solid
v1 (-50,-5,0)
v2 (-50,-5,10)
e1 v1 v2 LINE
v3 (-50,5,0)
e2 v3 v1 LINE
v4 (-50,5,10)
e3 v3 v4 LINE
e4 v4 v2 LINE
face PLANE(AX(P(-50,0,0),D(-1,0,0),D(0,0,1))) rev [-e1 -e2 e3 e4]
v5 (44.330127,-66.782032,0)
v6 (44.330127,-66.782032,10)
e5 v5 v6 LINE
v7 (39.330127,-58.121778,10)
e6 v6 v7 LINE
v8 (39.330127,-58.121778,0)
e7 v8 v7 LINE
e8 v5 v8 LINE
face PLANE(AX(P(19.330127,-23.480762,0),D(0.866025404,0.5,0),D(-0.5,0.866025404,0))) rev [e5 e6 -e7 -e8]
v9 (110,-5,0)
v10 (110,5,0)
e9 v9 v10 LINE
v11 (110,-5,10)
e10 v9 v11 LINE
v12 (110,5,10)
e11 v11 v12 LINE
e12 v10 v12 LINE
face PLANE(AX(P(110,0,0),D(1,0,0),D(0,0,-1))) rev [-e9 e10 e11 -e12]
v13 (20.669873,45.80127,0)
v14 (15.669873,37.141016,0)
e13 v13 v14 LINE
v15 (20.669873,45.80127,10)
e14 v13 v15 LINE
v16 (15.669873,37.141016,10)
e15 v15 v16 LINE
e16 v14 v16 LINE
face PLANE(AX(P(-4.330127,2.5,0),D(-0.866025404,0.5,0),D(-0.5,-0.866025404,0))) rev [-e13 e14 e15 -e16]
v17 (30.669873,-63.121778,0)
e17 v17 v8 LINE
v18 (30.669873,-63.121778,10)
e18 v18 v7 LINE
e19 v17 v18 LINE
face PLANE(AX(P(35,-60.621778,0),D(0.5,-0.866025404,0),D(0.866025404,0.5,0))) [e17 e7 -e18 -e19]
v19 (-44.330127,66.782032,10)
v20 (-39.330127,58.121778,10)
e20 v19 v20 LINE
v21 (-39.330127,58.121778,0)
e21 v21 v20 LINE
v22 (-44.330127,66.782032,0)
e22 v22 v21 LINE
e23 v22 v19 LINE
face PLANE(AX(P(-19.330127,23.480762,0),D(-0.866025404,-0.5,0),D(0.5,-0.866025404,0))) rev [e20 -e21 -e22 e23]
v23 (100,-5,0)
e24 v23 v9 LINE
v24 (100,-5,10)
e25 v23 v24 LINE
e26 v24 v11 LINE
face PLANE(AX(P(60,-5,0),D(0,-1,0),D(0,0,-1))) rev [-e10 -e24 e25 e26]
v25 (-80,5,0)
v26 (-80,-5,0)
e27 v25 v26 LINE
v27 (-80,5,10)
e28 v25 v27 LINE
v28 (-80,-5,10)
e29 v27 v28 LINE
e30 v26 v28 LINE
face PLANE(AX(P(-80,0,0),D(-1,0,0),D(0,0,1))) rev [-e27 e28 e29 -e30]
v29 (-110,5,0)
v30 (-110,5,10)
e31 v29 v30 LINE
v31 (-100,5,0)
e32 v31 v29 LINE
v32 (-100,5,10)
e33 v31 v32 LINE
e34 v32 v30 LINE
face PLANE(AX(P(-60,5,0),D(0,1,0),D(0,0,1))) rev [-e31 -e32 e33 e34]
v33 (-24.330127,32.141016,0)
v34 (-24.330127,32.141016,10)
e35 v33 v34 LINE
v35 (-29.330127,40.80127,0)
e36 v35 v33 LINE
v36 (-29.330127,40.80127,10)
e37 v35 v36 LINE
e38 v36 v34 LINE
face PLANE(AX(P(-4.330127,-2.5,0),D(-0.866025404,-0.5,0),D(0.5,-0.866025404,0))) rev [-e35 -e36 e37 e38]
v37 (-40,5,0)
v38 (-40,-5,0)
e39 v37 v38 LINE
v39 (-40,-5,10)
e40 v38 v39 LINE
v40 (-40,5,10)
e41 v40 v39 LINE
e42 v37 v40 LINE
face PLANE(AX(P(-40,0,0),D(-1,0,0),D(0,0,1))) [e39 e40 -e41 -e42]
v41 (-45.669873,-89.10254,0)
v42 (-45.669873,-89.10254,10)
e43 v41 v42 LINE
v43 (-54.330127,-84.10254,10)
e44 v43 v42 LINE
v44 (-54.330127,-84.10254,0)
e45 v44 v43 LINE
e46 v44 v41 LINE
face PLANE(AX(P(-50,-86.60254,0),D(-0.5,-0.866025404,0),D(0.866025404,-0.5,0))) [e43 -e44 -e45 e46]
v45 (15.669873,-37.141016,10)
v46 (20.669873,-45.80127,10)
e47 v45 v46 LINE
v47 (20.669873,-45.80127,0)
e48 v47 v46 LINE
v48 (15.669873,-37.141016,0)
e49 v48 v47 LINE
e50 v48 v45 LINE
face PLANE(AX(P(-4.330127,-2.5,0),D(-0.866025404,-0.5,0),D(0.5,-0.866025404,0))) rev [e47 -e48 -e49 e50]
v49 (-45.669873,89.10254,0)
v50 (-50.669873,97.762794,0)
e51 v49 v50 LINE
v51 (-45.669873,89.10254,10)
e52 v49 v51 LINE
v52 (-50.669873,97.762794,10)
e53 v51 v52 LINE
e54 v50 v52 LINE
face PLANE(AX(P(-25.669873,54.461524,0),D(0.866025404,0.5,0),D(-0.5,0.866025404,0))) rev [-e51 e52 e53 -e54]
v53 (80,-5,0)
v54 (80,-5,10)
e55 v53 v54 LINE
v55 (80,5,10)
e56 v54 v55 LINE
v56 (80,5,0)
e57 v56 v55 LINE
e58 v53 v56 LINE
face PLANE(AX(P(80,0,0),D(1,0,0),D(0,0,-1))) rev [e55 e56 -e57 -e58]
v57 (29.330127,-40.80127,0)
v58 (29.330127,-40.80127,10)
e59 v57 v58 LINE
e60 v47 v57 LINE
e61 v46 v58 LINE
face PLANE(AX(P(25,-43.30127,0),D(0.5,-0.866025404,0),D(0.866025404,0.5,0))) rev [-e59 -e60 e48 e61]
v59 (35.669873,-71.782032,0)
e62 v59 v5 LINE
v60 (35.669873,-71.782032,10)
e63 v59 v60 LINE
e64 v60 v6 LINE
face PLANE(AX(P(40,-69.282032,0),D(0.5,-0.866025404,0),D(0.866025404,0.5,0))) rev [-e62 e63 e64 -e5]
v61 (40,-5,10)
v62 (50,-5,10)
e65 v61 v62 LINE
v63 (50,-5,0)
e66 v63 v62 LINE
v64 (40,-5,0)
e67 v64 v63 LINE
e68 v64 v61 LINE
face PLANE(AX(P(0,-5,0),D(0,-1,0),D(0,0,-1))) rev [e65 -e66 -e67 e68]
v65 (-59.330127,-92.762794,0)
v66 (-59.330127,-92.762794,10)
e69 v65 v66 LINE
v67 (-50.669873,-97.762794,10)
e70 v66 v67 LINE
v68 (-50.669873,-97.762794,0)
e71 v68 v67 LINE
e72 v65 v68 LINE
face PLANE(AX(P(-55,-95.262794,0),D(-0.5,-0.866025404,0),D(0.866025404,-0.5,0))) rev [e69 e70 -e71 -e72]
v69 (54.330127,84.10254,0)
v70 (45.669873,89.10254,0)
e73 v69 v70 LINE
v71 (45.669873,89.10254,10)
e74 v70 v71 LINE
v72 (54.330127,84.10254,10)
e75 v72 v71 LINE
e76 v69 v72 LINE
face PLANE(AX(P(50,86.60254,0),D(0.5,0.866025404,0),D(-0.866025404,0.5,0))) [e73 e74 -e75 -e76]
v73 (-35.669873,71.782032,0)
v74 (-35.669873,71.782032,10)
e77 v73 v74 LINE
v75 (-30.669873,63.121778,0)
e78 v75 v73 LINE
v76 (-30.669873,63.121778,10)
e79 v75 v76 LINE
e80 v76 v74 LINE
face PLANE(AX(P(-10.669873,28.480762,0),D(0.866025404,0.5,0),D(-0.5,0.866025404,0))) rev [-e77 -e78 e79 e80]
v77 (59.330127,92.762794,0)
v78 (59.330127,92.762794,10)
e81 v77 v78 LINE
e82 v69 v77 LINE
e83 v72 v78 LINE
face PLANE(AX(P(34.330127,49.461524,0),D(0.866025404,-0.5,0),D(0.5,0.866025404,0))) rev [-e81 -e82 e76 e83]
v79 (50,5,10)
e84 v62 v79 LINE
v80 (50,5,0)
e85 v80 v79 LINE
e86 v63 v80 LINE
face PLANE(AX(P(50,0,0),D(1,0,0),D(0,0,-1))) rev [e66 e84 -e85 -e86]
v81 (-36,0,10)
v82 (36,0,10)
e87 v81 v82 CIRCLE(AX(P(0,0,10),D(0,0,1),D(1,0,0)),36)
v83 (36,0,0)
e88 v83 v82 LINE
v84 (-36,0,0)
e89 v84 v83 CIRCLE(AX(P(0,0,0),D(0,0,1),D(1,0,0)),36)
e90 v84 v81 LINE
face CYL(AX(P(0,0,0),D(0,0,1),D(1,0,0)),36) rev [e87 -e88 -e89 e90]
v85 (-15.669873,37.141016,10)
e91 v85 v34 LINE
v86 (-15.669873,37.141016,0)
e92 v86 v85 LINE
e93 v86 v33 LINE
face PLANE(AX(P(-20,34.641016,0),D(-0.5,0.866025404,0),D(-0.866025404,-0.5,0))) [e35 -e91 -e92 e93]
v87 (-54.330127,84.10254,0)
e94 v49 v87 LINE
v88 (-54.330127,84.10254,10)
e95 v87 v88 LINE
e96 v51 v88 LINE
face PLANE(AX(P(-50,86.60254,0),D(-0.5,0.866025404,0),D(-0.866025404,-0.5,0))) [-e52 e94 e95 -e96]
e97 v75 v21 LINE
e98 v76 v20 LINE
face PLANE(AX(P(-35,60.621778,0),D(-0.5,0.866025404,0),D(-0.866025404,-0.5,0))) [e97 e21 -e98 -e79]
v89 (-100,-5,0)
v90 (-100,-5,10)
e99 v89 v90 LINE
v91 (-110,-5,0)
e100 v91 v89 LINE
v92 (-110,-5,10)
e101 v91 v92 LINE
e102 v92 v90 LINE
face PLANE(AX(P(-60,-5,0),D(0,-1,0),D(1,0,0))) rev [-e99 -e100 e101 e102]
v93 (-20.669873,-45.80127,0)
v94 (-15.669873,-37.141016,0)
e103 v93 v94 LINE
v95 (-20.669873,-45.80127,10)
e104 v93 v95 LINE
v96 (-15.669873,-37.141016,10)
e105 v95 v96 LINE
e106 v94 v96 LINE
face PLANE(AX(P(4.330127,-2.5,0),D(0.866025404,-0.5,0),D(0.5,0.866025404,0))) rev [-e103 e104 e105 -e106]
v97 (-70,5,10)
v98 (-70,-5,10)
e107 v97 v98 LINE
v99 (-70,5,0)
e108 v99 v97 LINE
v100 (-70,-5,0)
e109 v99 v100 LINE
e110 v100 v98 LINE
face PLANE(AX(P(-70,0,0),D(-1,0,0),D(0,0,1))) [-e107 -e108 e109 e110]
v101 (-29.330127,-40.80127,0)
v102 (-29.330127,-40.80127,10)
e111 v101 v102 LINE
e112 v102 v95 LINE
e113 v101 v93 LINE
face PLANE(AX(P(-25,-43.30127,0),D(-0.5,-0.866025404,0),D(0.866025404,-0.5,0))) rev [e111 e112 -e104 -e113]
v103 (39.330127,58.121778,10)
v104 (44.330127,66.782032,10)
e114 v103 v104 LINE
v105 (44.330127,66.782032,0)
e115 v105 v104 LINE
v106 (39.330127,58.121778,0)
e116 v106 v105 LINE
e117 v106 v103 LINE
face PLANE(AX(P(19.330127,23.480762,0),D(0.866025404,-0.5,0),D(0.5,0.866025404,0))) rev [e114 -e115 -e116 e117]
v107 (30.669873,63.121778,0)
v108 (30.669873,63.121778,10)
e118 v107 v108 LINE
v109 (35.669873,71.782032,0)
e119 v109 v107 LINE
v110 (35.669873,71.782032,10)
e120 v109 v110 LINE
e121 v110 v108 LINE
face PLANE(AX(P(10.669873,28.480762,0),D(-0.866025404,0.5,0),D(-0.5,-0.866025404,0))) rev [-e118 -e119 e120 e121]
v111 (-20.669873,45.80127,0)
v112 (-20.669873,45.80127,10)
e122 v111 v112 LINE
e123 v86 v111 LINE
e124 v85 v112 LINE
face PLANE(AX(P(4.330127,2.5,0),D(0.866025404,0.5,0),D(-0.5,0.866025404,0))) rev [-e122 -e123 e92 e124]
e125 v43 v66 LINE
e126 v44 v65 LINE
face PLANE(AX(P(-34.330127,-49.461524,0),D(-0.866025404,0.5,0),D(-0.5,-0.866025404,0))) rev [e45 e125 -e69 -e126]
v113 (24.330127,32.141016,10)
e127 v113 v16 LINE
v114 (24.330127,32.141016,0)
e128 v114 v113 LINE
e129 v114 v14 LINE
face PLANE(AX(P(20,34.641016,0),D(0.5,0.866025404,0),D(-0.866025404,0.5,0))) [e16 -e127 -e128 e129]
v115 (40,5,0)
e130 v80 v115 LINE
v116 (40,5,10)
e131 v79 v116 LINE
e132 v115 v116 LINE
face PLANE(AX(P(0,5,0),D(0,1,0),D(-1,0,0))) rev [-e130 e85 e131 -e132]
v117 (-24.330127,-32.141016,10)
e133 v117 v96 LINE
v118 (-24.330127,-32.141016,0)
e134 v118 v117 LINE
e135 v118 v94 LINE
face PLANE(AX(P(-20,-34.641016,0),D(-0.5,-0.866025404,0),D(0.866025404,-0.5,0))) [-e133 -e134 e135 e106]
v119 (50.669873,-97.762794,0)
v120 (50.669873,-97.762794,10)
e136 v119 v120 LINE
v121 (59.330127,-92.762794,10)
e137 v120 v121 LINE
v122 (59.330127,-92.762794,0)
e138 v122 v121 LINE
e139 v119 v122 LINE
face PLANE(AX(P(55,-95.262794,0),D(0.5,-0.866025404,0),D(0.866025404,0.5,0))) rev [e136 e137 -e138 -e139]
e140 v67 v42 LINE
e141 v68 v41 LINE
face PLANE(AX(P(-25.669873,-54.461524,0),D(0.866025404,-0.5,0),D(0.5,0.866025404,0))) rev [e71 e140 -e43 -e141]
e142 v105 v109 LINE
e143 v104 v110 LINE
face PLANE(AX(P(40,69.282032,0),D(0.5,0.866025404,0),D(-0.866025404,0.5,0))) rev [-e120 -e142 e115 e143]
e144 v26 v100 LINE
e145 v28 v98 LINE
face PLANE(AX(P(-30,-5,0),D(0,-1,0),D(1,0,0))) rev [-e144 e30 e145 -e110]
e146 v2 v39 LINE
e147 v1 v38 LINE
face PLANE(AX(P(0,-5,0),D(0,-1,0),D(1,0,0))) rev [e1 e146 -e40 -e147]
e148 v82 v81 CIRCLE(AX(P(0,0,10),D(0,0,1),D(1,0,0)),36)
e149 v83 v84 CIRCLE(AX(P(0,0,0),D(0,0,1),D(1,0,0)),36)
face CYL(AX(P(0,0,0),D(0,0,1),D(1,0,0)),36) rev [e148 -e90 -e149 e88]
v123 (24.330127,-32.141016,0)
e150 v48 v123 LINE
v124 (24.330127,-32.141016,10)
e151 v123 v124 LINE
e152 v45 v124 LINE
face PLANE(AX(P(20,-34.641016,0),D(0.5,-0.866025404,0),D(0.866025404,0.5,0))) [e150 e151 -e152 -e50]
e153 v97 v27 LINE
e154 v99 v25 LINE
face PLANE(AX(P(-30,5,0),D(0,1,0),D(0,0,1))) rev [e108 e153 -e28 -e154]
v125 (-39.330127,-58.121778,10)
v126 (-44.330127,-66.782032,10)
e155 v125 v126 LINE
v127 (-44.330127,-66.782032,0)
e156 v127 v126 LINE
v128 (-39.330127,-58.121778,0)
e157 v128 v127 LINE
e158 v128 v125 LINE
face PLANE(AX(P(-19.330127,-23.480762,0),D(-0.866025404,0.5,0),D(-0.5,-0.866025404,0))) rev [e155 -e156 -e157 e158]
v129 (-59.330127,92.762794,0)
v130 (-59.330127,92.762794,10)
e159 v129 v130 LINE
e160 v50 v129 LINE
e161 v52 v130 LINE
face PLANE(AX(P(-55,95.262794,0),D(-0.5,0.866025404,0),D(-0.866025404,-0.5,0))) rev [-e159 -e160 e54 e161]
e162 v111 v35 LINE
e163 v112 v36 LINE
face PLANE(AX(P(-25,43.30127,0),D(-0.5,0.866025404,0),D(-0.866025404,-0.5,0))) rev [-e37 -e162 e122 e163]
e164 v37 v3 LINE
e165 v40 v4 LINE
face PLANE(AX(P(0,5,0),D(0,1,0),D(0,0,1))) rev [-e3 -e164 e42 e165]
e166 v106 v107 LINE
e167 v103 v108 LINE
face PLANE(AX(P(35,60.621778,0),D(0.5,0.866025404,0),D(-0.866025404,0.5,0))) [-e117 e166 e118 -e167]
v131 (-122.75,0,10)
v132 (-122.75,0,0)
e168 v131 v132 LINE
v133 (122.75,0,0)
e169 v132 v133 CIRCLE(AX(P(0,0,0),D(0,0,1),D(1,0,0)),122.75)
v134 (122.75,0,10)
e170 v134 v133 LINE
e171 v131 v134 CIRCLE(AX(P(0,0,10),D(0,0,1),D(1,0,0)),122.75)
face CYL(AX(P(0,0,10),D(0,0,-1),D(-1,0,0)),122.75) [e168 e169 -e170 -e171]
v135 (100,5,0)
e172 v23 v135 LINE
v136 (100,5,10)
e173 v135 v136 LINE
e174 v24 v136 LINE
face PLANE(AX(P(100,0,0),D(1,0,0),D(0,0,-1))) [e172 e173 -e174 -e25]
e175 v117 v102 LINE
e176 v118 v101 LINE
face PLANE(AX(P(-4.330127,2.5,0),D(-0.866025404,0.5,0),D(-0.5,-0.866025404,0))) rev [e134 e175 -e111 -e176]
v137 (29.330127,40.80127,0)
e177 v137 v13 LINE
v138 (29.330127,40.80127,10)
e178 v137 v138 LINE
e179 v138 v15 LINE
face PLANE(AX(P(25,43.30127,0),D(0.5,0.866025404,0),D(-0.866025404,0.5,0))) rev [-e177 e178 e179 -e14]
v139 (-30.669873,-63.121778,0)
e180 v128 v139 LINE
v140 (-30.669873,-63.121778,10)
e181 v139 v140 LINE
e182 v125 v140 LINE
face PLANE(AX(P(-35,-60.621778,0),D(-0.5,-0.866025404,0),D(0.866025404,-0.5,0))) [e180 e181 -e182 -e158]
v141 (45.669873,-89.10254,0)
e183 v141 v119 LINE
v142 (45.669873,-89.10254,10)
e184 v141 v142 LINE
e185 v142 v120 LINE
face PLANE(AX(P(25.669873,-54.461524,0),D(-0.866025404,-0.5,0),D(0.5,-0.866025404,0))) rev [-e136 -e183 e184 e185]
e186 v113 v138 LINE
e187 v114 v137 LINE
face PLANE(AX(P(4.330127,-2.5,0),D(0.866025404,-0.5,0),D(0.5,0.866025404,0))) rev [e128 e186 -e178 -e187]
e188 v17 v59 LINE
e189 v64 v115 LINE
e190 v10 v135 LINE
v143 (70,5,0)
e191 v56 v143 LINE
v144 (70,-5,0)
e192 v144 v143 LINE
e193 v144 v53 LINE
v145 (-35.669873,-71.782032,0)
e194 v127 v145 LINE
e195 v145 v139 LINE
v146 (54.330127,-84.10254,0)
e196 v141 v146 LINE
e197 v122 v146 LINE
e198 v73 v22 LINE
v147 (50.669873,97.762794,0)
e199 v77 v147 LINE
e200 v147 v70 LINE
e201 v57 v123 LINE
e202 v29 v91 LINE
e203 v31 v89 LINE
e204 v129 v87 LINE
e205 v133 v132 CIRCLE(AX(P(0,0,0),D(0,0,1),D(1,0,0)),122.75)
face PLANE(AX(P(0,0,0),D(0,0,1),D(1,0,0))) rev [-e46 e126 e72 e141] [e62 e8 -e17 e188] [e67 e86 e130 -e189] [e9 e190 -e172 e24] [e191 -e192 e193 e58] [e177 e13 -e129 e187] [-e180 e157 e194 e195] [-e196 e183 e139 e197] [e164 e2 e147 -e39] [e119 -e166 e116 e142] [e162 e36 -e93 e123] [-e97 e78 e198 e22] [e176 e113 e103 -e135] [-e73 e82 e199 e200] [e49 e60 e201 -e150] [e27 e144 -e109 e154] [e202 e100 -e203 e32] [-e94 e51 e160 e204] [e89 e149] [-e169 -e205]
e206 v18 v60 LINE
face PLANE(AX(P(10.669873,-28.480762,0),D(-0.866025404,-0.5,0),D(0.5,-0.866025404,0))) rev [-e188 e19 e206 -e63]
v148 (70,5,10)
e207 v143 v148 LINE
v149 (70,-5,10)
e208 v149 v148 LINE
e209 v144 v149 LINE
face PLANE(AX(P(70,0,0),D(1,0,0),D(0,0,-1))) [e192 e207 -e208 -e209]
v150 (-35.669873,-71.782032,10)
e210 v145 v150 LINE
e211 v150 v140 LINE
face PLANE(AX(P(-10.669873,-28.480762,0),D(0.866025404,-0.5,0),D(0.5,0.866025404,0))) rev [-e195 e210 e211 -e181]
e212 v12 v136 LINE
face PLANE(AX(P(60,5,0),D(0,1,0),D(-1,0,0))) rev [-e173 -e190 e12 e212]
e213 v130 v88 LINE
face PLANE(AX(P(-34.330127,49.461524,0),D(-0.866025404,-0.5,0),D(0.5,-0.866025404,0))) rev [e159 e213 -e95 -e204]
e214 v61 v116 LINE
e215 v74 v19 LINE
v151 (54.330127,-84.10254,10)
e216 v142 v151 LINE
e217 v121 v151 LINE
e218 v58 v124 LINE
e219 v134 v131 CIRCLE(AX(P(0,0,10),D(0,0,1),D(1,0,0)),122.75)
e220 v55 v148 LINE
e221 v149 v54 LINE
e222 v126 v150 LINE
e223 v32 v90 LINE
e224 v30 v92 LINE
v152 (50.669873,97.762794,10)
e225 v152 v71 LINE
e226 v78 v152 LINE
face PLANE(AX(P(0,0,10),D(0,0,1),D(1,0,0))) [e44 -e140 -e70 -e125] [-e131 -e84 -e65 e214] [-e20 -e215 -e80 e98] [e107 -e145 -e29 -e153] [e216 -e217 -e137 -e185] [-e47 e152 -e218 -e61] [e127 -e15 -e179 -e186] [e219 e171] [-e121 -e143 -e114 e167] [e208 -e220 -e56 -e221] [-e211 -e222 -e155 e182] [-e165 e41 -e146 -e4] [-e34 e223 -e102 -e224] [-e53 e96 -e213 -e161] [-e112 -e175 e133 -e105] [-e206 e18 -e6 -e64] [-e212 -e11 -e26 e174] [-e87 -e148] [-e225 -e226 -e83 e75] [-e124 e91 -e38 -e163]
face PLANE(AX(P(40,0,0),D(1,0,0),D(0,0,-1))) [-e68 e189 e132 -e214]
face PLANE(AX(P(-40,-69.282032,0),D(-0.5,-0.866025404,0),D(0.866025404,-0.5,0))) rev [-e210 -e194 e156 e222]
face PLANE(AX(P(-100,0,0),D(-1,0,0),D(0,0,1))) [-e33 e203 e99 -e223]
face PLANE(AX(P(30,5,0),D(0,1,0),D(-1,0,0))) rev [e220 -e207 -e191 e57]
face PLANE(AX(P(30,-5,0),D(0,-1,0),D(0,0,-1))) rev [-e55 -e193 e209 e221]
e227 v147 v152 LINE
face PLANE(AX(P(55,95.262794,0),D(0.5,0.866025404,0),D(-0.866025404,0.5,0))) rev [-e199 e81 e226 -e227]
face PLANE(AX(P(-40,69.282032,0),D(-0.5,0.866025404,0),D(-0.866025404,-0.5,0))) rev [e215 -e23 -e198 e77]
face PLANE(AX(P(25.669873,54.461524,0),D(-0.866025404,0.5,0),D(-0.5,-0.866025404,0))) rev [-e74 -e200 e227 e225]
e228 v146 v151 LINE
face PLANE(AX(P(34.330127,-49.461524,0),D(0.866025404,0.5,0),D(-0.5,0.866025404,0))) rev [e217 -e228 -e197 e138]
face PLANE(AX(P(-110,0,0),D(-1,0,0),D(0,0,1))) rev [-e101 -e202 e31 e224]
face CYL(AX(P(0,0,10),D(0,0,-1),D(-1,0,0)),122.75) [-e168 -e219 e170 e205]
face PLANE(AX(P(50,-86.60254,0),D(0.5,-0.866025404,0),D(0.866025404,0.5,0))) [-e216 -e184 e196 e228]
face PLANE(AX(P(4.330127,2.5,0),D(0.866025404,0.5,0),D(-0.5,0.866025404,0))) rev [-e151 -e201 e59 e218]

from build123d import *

# Parameters (mm, degrees)
PLATE_PROFILE_245_5_R                        = 122.75
PLATE_DISC_245_5X10_DEPTH                    = 10
CENTRE_BORE_PROFILE_72_R                     = 36
CENTRE_BORE_72_DEPTH                         = 174.882503433
WINDOW_CUT_DEPTH                             = 174.882503433
INNER_WINDOW_CIRCULAR_PATTERN_6X_COUNT       = 6
WINDOW_RADIAL_ROW_3X30_COUNT                 = 3
WINDOW_RADIAL_ROW_3X30_PITCH                 = 30
WINDOW_ROW_CIRCULAR_PATTERN_6X_COPY_1_DEPTH  = 174.882503433
WINDOW_ROW_CIRCULAR_PATTERN_6X_COPY_2_DEPTH  = 174.882503433
WINDOW_ROW_CIRCULAR_PATTERN_6X_COPY_3_DEPTH  = 174.882503433
WINDOW_ROW_CIRCULAR_PATTERN_6X_COPY_4_DEPTH  = 174.882503433
WINDOW_ROW_CIRCULAR_PATTERN_6X_COPY_5_DEPTH  = 174.882503433
WINDOW_ROW_CIRCULAR_PATTERN_6X_COPY_6_DEPTH  = 174.882503433
WINDOW_ROW_CIRCULAR_PATTERN_6X_COPY_7_DEPTH  = 174.882503433
WINDOW_ROW_CIRCULAR_PATTERN_6X_COPY_8_DEPTH  = 174.882503433
WINDOW_ROW_CIRCULAR_PATTERN_6X_COPY_9_DEPTH  = 174.882503433
WINDOW_ROW_CIRCULAR_PATTERN_6X_COPY_10_DEPTH = 174.882503433
WINDOW_ROW_CIRCULAR_PATTERN_6X_COPY_11_DEPTH = 174.882503433
WINDOW_ROW_CIRCULAR_PATTERN_6X_COPY_12_DEPTH = 174.882503433
WINDOW_ROW_CIRCULAR_PATTERN_6X_COPY_13_DEPTH = 174.882503433
WINDOW_ROW_CIRCULAR_PATTERN_6X_COPY_14_DEPTH = 174.882503433
WINDOW_ROW_CIRCULAR_PATTERN_6X_COPY_15_DEPTH = 174.882503433


with BuildPart() as part:
    # Plate Profile Ø245.5 → Plate Disc Ø245.5x10 (new body)
    with BuildSketch(Plane.XY):
        Circle(PLATE_PROFILE_245_5_R)
    extrude(amount=PLATE_DISC_245_5X10_DEPTH)

    # Centre Bore Profile Ø72 → Centre Bore Ø72 (cut, through all)
    with BuildSketch(Plane.XY.offset(10)):
        Circle(CENTRE_BORE_PROFILE_72_R)
    extrude(amount=-CENTRE_BORE_72_DEPTH, mode=Mode.SUBTRACT)

    # Window Profile → Window Cut (cut, through all)
    with BuildSketch(Plane.XY.offset(10)):
        Polygon((50, -5), (50, 5), (40, 5), (40, 0), (40, -5), align=None)
    window_cut = extrude(amount=-WINDOW_CUT_DEPTH, mode=Mode.SUBTRACT)

    # Inner Window Circular Pattern 6x: Window Cut ×6 about axis
    inner_window_circular_pattern_6x_axis = Axis((0, 0, 0), (0, 0, 1))
    for i in range(1, INNER_WINDOW_CIRCULAR_PATTERN_6X_COUNT):
        add(window_cut.rotate(inner_window_circular_pattern_6x_axis, i * 360 / INNER_WINDOW_CIRCULAR_PATTERN_6X_COUNT), mode=Mode.SUBTRACT)

    # Window Radial Row 3x30: Window Cut ×3
    with Locations(*[(i * WINDOW_RADIAL_ROW_3X30_PITCH, 0, 0) for i in range(1, WINDOW_RADIAL_ROW_3X30_COUNT)]):
        add(window_cut, mode=Mode.SUBTRACT)

    # Window Row Circular Pattern 6x copy 1 sk → Window Row Circular Pattern 6x copy 1 (cut, through all)
    with BuildSketch(Plane(origin=(15, 25.980762114, 10), x_dir=(0.5000000000000001, 0.8660254037844386, 0), z_dir=(0, 0, 1))):
        Polygon((50, -5), (50, 5), (40, 5), (40, 0), (40, -5), align=None)
    extrude(amount=-WINDOW_ROW_CIRCULAR_PATTERN_6X_COPY_1_DEPTH, mode=Mode.SUBTRACT)

    # Window Row Circular Pattern 6x copy 2 sk → Window Row Circular Pattern 6x copy 2 (cut, through all)
    with BuildSketch(Plane(origin=(-15, 25.980762114, 10), x_dir=(-0.4999999999999998, 0.8660254037844387, 0), z_dir=(0, 0, 1))):
        Polygon((50, -5), (50, 5), (40, 5), (40, 0), (40, -5), align=None)
    extrude(amount=-WINDOW_ROW_CIRCULAR_PATTERN_6X_COPY_2_DEPTH, mode=Mode.SUBTRACT)

    # Window Row Circular Pattern 6x copy 3 sk → Window Row Circular Pattern 6x copy 3 (cut, through all)
    with BuildSketch(Plane(origin=(-30, 0, 10), x_dir=(-1, 0, 0), z_dir=(0, 0, 1))):
        Polygon((50, -5), (50, 5), (40, 5), (40, 0), (40, -5), align=None)
    extrude(amount=-WINDOW_ROW_CIRCULAR_PATTERN_6X_COPY_3_DEPTH, mode=Mode.SUBTRACT)

    # Window Row Circular Pattern 6x copy 4 sk → Window Row Circular Pattern 6x copy 4 (cut, through all)
    with BuildSketch(Plane(origin=(-15, -25.980762114, 10), x_dir=(-0.5000000000000004, -0.8660254037844384, 0), z_dir=(0, 0, 1))):
        Polygon((50, -5), (50, 5), (40, 5), (40, 0), (40, -5), align=None)
    extrude(amount=-WINDOW_ROW_CIRCULAR_PATTERN_6X_COPY_4_DEPTH, mode=Mode.SUBTRACT)

    # Window Row Circular Pattern 6x copy 5 sk → Window Row Circular Pattern 6x copy 5 (cut, through all)
    with BuildSketch(Plane(origin=(15, -25.980762114, 10), x_dir=(0.5000000000000001, -0.8660254037844386, 0), z_dir=(0, 0, 1))):
        Polygon((50, -5), (50, 5), (40, 5), (40, 0), (40, -5), align=None)
    extrude(amount=-WINDOW_ROW_CIRCULAR_PATTERN_6X_COPY_5_DEPTH, mode=Mode.SUBTRACT)

    # Window Row Circular Pattern 6x copy 6 sk → Window Row Circular Pattern 6x copy 6 (cut, through all)
    with BuildSketch(Plane(origin=(30, 51.961524227, 10), x_dir=(0.5000000000000001, 0.8660254037844386, 0), z_dir=(0, 0, 1))):
        Polygon((50, -5), (50, 5), (40, 5), (40, 0), (40, -5), align=None)
    extrude(amount=-WINDOW_ROW_CIRCULAR_PATTERN_6X_COPY_6_DEPTH, mode=Mode.SUBTRACT)

    # Window Row Circular Pattern 6x copy 7 sk → Window Row Circular Pattern 6x copy 7 (cut, through all)
    with BuildSketch(Plane(origin=(-30, 51.961524227, 10), x_dir=(-0.4999999999999998, 0.8660254037844387, 0), z_dir=(0, 0, 1))):
        Polygon((50, -5), (50, 5), (40, 5), (40, 0), (40, -5), align=None)
    extrude(amount=-WINDOW_ROW_CIRCULAR_PATTERN_6X_COPY_7_DEPTH, mode=Mode.SUBTRACT)

    # Window Row Circular Pattern 6x copy 8 sk → Window Row Circular Pattern 6x copy 8 (cut, through all)
    with BuildSketch(Plane(origin=(-60, 0, 10), x_dir=(-1, 0, 0), z_dir=(0, 0, 1))):
        Polygon((50, -5), (50, 5), (40, 5), (40, 0), (40, -5), align=None)
    extrude(amount=-WINDOW_ROW_CIRCULAR_PATTERN_6X_COPY_8_DEPTH, mode=Mode.SUBTRACT)

    # Window Row Circular Pattern 6x copy 9 sk → Window Row Circular Pattern 6x copy 9 (cut, through all)
    with BuildSketch(Plane(origin=(-30, -51.961524227, 10), x_dir=(-0.5000000000000004, -0.8660254037844384, 0), z_dir=(0, 0, 1))):
        Polygon((50, -5), (50, 5), (40, 5), (40, 0), (40, -5), align=None)
    extrude(amount=-WINDOW_ROW_CIRCULAR_PATTERN_6X_COPY_9_DEPTH, mode=Mode.SUBTRACT)

    # Window Row Circular Pattern 6x copy 10 s → Window Row Circular Pattern 6x copy 10 (cut, through all)
    with BuildSketch(Plane(origin=(30, -51.961524227, 10), x_dir=(0.5000000000000001, -0.8660254037844386, 0), z_dir=(0, 0, 1))):
        Polygon((50, -5), (50, 5), (40, 5), (40, 0), (40, -5), align=None)
    extrude(amount=-WINDOW_ROW_CIRCULAR_PATTERN_6X_COPY_10_DEPTH, mode=Mode.SUBTRACT)

    # Window Row Circular Pattern 6x copy 11 s → Window Row Circular Pattern 6x copy 11 (cut, through all)
    with BuildSketch(Plane(origin=(0, 0, 10), x_dir=(0.5000000000000001, 0.8660254037844386, 0), z_dir=(0, 0, 1))):
        Polygon((50, -5), (50, 5), (40, 5), (40, 0), (40, -5), align=None)
    extrude(amount=-WINDOW_ROW_CIRCULAR_PATTERN_6X_COPY_11_DEPTH, mode=Mode.SUBTRACT)

    # Window Row Circular Pattern 6x copy 12 s → Window Row Circular Pattern 6x copy 12 (cut, through all)
    with BuildSketch(Plane(origin=(0, 0, 10), x_dir=(-0.4999999999999998, 0.8660254037844387, 0), z_dir=(0, 0, 1))):
        Polygon((50, -5), (50, 5), (40, 5), (40, 0), (40, -5), align=None)
    extrude(amount=-WINDOW_ROW_CIRCULAR_PATTERN_6X_COPY_12_DEPTH, mode=Mode.SUBTRACT)

    # Window Row Circular Pattern 6x copy 13 s → Window Row Circular Pattern 6x copy 13 (cut, through all)
    with BuildSketch(Plane(origin=(0, 0, 10), x_dir=(-1, 0, 0), z_dir=(0, 0, 1))):
        Polygon((50, -5), (50, 5), (40, 5), (40, 0), (40, -5), align=None)
    extrude(amount=-WINDOW_ROW_CIRCULAR_PATTERN_6X_COPY_13_DEPTH, mode=Mode.SUBTRACT)

    # Window Row Circular Pattern 6x copy 14 s → Window Row Circular Pattern 6x copy 14 (cut, through all)
    with BuildSketch(Plane(origin=(0, 0, 10), x_dir=(-0.5000000000000004, -0.8660254037844384, 0), z_dir=(0, 0, 1))):
        Polygon((50, -5), (50, 5), (40, 5), (40, 0), (40, -5), align=None)
    extrude(amount=-WINDOW_ROW_CIRCULAR_PATTERN_6X_COPY_14_DEPTH, mode=Mode.SUBTRACT)

    # Window Row Circular Pattern 6x copy 15 s → Window Row Circular Pattern 6x copy 15 (cut, through all)
    with BuildSketch(Plane(origin=(0, 0, 10), x_dir=(0.5000000000000001, -0.8660254037844386, 0), z_dir=(0, 0, 1))):
        Polygon((50, -5), (50, 5), (40, 5), (40, 0), (40, -5), align=None)
    extrude(amount=-WINDOW_ROW_CIRCULAR_PATTERN_6X_COPY_15_DEPTH, mode=Mode.SUBTRACT)


solid = part.part
